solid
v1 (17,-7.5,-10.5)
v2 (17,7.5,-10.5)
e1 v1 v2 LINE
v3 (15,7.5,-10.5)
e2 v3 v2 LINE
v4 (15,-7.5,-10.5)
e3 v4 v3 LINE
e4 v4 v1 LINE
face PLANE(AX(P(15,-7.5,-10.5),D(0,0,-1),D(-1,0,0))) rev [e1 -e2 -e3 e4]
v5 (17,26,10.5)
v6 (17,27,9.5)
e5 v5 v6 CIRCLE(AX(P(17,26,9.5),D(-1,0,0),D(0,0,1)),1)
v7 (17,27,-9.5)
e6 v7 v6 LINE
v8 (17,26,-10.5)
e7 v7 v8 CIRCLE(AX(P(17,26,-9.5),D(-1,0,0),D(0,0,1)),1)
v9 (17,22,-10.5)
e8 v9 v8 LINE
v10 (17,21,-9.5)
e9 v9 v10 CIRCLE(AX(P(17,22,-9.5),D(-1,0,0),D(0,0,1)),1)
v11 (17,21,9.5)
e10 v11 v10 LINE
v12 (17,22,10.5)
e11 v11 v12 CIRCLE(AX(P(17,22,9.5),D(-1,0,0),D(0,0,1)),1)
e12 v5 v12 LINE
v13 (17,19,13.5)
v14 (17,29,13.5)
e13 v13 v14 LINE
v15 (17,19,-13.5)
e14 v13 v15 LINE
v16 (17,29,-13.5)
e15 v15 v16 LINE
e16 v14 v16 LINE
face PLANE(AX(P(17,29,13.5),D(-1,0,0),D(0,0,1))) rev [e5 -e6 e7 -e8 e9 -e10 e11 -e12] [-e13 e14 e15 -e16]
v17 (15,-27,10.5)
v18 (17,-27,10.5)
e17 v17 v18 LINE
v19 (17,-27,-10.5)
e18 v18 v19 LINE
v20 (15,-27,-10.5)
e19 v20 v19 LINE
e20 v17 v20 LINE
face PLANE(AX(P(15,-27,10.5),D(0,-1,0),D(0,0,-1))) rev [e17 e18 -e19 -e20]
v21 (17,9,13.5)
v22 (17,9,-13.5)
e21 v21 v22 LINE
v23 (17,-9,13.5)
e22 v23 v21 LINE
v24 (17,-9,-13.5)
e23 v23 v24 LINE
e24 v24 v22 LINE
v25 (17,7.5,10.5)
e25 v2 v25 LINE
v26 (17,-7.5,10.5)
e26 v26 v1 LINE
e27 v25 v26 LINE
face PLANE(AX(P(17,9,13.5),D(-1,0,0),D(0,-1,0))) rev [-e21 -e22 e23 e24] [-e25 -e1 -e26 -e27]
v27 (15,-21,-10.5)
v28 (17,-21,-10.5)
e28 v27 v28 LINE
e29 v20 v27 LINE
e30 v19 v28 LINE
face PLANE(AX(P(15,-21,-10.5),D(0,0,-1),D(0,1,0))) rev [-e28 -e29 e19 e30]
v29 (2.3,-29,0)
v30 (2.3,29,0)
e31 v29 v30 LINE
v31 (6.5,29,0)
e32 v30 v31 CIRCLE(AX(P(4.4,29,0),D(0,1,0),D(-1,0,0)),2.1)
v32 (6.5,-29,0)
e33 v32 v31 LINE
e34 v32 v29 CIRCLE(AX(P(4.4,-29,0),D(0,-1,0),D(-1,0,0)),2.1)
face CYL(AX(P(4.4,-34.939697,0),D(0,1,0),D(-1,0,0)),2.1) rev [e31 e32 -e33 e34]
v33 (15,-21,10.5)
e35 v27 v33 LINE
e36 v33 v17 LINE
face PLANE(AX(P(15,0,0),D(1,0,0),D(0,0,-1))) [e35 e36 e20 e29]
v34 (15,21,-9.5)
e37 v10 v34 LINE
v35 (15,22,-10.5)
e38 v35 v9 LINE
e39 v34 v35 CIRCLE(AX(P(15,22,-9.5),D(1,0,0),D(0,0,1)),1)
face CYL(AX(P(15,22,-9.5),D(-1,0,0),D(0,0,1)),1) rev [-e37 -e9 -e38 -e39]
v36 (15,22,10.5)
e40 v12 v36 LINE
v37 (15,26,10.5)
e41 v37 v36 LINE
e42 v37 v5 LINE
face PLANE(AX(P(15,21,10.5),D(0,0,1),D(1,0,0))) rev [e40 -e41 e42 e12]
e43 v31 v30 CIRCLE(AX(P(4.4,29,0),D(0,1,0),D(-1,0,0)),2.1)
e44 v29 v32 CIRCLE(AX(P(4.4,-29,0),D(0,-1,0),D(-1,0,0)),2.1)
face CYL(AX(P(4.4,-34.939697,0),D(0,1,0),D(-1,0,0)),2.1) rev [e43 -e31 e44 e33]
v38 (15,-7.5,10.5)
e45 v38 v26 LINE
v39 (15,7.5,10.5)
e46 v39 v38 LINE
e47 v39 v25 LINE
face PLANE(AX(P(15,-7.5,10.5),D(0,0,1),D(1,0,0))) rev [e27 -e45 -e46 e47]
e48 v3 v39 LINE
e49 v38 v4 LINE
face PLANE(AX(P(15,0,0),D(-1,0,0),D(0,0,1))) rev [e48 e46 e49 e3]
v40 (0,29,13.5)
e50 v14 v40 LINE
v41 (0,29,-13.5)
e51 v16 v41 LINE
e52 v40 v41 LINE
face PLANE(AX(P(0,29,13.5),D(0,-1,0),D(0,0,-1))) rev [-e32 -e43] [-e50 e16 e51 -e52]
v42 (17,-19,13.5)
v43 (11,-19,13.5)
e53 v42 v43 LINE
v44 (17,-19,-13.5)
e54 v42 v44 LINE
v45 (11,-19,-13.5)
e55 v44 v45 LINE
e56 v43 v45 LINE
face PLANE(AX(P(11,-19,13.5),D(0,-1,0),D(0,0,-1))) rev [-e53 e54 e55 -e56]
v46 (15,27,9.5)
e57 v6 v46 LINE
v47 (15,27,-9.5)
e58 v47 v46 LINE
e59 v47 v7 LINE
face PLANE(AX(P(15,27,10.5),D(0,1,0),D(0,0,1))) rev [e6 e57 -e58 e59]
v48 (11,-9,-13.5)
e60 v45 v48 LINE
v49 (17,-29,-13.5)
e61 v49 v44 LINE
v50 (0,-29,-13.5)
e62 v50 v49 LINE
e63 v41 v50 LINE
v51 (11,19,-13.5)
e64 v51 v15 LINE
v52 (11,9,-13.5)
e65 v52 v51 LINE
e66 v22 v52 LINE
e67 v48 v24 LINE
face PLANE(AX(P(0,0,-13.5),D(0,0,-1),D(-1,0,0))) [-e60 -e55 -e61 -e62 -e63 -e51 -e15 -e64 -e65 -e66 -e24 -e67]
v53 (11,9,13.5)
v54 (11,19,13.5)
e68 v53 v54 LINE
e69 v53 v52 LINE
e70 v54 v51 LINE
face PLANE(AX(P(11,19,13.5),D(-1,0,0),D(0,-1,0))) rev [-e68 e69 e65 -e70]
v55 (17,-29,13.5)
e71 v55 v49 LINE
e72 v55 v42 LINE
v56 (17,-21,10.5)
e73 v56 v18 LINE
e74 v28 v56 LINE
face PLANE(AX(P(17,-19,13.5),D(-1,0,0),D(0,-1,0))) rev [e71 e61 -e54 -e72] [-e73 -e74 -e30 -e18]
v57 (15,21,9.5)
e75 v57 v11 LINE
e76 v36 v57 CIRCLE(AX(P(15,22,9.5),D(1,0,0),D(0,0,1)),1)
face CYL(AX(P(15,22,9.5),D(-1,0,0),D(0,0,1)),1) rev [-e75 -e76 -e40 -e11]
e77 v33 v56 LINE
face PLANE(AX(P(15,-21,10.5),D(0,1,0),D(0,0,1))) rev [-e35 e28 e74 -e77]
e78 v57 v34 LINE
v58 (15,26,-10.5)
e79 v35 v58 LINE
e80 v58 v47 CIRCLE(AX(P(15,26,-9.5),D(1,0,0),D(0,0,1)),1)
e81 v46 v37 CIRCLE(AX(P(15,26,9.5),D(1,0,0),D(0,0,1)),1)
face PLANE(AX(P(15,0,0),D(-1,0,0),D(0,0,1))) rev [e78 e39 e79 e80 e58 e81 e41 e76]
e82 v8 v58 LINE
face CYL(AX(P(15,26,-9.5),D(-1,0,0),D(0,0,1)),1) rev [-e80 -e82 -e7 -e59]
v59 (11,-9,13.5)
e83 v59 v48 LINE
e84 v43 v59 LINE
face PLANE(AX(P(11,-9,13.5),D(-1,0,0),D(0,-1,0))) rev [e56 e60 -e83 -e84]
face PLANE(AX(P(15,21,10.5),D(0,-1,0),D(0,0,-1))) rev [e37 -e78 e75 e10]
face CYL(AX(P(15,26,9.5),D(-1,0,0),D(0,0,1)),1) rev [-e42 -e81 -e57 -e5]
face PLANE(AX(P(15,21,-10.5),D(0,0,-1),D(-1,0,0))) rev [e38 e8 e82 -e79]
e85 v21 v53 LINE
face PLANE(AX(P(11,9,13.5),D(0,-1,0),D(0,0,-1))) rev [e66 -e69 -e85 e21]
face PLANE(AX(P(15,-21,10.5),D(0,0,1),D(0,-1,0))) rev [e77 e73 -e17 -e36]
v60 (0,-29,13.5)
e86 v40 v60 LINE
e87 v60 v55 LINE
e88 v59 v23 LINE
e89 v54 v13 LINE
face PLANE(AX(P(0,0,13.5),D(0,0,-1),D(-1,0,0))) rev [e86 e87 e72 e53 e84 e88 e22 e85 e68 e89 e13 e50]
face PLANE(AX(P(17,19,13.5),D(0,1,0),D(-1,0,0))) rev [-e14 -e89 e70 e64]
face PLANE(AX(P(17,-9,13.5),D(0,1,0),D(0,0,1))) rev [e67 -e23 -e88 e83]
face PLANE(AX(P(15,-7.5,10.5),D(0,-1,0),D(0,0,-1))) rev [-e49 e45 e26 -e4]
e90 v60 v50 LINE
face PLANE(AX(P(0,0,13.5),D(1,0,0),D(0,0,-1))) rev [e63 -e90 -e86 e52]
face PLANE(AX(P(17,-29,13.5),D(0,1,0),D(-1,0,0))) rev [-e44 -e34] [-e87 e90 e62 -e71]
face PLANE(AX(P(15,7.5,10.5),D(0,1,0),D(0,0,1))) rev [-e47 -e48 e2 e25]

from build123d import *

# Parameters (mm, degrees)
EXTRUDE_1_DEPTH        = 13.5
SKETCH_2_W             = 21
SKETCH_2_H             = 6
SKETCH_2_H_2           = 15
CUT_EXTRUDE_1_DEPTH    = 2
FILLET_1_R             = 1
SKETCH_3_R             = 2.1
CUT_EXTRUDE_2_DEPTH    = 58
HOLE_WIZARD_M5_1_D     = 4.2
HOLE_WIZARD_M5_1_DEPTH = 8
HOLE_WIZARD_M5_1_TIP   = 1.2618073


with BuildPart() as part:
    # 草图1 → 凸台-拉伸1 (new, symmetric)
    with BuildSketch(Plane.XY):
        Polygon((0, 0), (0, 29), (17, 29), (17, 19), (11, 19), (11, 9), (17, 9), (17, -9), (11, -9), (11, -19), (17, -19), (17, -29), (0, -29), align=None)
    extrude(amount=EXTRUDE_1_DEPTH, both=True)

    # 草图2 → 切除-拉伸1 (cut)
    with BuildSketch(Plane(origin=(17, 0, 0), x_dir=(0, 0, -1), z_dir=(1, 0, 0))):
        with Locations((0, 24)):
            Rectangle(SKETCH_2_W, SKETCH_2_H)
        Rectangle(SKETCH_2_W, SKETCH_2_H_2)
        with Locations((0, -24)):
            Rectangle(SKETCH_2_W, SKETCH_2_H)
    extrude(amount=-CUT_EXTRUDE_1_DEPTH, mode=Mode.SUBTRACT)

    # 圆角1
    fillet_1_edges = [part.edges().sort_by_distance(p)[0] for p in [
        (16, 27, -10.5),
        (16, 21, -10.5),
        (16, 21, 10.5),
        (16, 27, 10.5),
    ]]
    fillet(fillet_1_edges, radius=FILLET_1_R)

    # 草图3 → 切除-拉伸2 (cut)
    with BuildSketch(Plane(origin=(0, 29, 0), x_dir=(1, 0, 0), z_dir=(0, 1, 0))):
        with Locations(Location((4.4, 0, 0), (0, 0, 180))):
            Circle(SKETCH_3_R)
    extrude(amount=-CUT_EXTRUDE_2_DEPTH, mode=Mode.SUBTRACT)

    # M5 螺纹孔1
    with Locations(Plane(origin=(4.4, 29, 0), x_dir=(0, 0, 1), z_dir=(0, 1, 0))):
        with Locations((0, 0)):
            Hole(HOLE_WIZARD_M5_1_D / 2, depth=HOLE_WIZARD_M5_1_DEPTH)
            with Locations((0, 0, -(HOLE_WIZARD_M5_1_DEPTH + HOLE_WIZARD_M5_1_TIP / 2))):  # 118° drill point
                Cone(0, HOLE_WIZARD_M5_1_D / 2, HOLE_WIZARD_M5_1_TIP, mode=Mode.SUBTRACT)


solid = part.part
